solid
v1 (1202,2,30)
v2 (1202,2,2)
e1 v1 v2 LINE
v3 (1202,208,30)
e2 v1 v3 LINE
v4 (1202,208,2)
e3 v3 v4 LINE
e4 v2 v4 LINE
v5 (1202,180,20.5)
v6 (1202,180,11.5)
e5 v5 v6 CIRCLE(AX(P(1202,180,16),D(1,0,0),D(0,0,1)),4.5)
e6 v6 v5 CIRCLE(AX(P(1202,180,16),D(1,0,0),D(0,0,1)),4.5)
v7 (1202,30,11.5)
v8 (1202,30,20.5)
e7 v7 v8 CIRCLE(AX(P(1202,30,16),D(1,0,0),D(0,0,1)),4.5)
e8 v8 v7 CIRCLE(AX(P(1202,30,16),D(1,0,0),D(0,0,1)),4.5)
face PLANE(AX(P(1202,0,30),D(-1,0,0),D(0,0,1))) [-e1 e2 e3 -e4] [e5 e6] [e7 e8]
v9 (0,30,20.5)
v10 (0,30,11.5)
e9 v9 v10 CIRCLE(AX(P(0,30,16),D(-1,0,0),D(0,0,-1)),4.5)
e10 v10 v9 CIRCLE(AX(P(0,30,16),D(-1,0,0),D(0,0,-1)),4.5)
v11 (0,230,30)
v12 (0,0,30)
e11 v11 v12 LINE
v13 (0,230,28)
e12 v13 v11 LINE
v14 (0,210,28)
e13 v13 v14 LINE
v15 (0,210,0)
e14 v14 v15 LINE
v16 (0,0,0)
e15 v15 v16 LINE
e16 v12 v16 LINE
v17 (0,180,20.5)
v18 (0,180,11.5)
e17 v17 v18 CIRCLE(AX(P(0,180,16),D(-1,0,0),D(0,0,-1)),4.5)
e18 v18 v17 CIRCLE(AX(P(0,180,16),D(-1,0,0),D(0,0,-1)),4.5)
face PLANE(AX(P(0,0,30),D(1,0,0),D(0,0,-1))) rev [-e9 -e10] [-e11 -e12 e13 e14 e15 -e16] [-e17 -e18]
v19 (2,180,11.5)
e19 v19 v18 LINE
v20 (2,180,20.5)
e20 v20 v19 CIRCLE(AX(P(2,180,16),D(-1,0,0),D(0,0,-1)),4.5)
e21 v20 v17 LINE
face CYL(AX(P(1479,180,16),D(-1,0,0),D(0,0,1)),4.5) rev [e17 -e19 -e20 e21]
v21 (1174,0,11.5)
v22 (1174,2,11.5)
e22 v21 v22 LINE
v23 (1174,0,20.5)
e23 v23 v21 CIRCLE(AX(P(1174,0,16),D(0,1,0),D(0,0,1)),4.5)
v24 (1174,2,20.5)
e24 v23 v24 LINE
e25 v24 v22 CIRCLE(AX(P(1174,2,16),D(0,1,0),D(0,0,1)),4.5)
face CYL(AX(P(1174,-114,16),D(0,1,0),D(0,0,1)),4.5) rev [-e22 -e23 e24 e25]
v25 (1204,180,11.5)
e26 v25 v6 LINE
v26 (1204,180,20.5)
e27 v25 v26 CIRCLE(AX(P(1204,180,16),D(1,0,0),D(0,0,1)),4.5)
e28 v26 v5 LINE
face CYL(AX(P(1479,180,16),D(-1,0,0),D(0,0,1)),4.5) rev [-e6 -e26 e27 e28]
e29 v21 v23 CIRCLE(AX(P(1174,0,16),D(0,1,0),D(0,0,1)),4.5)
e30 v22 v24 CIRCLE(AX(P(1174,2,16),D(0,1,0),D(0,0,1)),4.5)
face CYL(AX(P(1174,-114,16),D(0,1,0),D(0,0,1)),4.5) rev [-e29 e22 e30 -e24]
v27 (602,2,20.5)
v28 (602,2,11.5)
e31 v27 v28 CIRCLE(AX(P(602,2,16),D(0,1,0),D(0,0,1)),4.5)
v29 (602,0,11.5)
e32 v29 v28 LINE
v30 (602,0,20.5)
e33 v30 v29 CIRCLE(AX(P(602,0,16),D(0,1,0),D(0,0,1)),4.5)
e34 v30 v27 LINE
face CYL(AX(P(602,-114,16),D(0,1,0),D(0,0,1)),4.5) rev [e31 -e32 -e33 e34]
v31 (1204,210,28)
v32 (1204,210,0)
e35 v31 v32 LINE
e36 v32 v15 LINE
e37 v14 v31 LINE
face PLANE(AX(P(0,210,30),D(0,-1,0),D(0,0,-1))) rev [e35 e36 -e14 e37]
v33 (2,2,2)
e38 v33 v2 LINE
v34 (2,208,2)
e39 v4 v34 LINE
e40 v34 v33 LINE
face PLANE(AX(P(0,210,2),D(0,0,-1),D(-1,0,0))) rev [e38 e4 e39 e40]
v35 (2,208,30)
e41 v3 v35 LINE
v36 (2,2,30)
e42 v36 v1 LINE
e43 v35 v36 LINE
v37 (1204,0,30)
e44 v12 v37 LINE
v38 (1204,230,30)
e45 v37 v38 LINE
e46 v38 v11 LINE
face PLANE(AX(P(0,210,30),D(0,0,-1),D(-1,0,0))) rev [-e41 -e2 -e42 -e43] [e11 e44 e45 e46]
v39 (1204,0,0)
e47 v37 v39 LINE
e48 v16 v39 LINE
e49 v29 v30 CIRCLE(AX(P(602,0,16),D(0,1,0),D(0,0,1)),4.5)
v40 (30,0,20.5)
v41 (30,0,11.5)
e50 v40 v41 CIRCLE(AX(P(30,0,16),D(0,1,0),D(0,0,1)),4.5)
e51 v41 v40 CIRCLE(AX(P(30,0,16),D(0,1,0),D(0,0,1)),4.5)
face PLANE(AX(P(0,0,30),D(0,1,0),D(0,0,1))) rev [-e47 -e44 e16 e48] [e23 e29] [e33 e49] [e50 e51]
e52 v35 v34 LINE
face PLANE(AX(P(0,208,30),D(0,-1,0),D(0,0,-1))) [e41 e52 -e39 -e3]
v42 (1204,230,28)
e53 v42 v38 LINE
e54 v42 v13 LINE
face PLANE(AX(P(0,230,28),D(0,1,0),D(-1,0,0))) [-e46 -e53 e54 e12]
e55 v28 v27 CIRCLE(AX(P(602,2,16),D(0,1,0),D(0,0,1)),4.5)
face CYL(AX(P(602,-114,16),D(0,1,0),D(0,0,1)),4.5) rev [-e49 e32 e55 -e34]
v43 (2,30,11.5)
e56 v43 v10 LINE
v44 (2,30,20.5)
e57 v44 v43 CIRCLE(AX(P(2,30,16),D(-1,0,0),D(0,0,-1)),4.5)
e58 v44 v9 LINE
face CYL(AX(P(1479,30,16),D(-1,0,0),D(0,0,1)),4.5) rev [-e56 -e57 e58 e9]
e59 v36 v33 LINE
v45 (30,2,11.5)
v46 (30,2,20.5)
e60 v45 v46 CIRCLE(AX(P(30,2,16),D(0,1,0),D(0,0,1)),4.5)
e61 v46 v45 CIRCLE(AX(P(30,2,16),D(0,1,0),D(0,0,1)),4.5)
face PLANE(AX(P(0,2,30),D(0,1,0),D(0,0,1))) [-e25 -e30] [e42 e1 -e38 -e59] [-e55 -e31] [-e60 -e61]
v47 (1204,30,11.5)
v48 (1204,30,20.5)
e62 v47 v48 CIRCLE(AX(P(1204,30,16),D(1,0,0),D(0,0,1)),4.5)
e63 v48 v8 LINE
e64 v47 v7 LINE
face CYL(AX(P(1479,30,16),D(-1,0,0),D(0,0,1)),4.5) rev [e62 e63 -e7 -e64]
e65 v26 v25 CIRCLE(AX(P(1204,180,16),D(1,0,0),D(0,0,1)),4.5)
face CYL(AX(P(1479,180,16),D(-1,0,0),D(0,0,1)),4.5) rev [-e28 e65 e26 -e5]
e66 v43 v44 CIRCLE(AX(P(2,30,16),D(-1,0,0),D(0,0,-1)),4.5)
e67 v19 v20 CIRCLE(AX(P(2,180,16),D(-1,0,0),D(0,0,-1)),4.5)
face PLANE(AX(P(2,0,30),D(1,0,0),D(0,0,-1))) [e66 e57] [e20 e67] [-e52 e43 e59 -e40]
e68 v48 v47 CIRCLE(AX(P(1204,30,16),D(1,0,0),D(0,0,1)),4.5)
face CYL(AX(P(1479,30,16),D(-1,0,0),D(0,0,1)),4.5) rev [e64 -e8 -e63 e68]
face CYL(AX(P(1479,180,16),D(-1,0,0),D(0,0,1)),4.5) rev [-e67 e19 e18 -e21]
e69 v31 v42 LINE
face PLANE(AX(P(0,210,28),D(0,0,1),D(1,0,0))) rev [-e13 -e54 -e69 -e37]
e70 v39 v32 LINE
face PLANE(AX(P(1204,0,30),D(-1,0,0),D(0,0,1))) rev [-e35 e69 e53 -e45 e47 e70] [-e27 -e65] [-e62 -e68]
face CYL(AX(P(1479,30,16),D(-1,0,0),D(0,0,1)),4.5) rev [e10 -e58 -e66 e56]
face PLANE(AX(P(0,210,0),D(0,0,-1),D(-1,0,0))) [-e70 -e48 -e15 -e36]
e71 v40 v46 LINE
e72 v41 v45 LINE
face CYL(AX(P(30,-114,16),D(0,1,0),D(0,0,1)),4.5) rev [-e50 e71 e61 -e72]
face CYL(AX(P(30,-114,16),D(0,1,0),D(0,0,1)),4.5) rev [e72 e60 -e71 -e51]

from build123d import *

# Parameters (mm, degrees)
SKETCH_1_W               = 1204
SKETCH_1_H               = 210
EXTRUDE_1_DEPTH          = 30
SHELL_1_T                = -2
SKETCH_2_W               = 1204
SKETCH_2_H               = 20
EXTRUDE_2_DEPTH          = 2
CUT_EXTRUDE_1_DEPTH      = 1477
CUT_EXTRUDE_1_DEPTH_BACK = 116
SKETCH_3_R               = 4.5
SKETCH_4_R               = 4.5
CUT_EXTRUDE_2_DEPTH      = 116


with BuildPart() as part:
    # 草图1 → 凸台-拉伸1 (new body)
    with BuildSketch(Plane.XY):
        with Locations((602, 105)):
            Rectangle(SKETCH_1_W, SKETCH_1_H)
    extrude(amount=EXTRUDE_1_DEPTH)

    # 抽壳1
    shell_1_openings = [part.faces().sort_by_distance(p)[0] for p in [
        (602, 105, 30),
    ]]
    offset(amount=SHELL_1_T, openings=shell_1_openings, kind=Kind.INTERSECTION)

    # 草图2 → 凸台-拉伸2 (add)
    with BuildSketch(Plane.XY.offset(30)):
        with Locations((602, 220)):
            Rectangle(SKETCH_2_W, SKETCH_2_H)
    extrude(amount=-EXTRUDE_2_DEPTH)

    # 草图3 → 切除-拉伸1 (cut, two sides: drawn at the far end of the back side and taken through both)
    with BuildSketch(Plane(origin=(2, 0, 0), x_dir=(0, 0, -1), z_dir=(1, 0, 0)).offset(-CUT_EXTRUDE_1_DEPTH_BACK)):
        with Locations(Location((-16, 180, 0), (0, 0, 180))):
            Circle(SKETCH_3_R)
        with Locations(Location((-16, 30, 0), (0, 0, 180))):
            Circle(SKETCH_3_R)
    extrude(amount=CUT_EXTRUDE_1_DEPTH + CUT_EXTRUDE_1_DEPTH_BACK, mode=Mode.SUBTRACT)

    # 草图4 → 切除-拉伸2 (cut)
    with BuildSketch(Plane(origin=(0, 2, 0), x_dir=(1, 0, 0), z_dir=(0, 1, 0))):
        with Locations(Location((30, -16, 0), (0, 0, 270))):
            Circle(SKETCH_4_R)
        with Locations(Location((1174, -16, 0), (0, 0, 270))):
            Circle(SKETCH_4_R)
        with Locations(Location((602, -16, 0), (0, 0, 270))):
            Circle(SKETCH_4_R)
    extrude(amount=-CUT_EXTRUDE_2_DEPTH, mode=Mode.SUBTRACT)


solid = part.part
